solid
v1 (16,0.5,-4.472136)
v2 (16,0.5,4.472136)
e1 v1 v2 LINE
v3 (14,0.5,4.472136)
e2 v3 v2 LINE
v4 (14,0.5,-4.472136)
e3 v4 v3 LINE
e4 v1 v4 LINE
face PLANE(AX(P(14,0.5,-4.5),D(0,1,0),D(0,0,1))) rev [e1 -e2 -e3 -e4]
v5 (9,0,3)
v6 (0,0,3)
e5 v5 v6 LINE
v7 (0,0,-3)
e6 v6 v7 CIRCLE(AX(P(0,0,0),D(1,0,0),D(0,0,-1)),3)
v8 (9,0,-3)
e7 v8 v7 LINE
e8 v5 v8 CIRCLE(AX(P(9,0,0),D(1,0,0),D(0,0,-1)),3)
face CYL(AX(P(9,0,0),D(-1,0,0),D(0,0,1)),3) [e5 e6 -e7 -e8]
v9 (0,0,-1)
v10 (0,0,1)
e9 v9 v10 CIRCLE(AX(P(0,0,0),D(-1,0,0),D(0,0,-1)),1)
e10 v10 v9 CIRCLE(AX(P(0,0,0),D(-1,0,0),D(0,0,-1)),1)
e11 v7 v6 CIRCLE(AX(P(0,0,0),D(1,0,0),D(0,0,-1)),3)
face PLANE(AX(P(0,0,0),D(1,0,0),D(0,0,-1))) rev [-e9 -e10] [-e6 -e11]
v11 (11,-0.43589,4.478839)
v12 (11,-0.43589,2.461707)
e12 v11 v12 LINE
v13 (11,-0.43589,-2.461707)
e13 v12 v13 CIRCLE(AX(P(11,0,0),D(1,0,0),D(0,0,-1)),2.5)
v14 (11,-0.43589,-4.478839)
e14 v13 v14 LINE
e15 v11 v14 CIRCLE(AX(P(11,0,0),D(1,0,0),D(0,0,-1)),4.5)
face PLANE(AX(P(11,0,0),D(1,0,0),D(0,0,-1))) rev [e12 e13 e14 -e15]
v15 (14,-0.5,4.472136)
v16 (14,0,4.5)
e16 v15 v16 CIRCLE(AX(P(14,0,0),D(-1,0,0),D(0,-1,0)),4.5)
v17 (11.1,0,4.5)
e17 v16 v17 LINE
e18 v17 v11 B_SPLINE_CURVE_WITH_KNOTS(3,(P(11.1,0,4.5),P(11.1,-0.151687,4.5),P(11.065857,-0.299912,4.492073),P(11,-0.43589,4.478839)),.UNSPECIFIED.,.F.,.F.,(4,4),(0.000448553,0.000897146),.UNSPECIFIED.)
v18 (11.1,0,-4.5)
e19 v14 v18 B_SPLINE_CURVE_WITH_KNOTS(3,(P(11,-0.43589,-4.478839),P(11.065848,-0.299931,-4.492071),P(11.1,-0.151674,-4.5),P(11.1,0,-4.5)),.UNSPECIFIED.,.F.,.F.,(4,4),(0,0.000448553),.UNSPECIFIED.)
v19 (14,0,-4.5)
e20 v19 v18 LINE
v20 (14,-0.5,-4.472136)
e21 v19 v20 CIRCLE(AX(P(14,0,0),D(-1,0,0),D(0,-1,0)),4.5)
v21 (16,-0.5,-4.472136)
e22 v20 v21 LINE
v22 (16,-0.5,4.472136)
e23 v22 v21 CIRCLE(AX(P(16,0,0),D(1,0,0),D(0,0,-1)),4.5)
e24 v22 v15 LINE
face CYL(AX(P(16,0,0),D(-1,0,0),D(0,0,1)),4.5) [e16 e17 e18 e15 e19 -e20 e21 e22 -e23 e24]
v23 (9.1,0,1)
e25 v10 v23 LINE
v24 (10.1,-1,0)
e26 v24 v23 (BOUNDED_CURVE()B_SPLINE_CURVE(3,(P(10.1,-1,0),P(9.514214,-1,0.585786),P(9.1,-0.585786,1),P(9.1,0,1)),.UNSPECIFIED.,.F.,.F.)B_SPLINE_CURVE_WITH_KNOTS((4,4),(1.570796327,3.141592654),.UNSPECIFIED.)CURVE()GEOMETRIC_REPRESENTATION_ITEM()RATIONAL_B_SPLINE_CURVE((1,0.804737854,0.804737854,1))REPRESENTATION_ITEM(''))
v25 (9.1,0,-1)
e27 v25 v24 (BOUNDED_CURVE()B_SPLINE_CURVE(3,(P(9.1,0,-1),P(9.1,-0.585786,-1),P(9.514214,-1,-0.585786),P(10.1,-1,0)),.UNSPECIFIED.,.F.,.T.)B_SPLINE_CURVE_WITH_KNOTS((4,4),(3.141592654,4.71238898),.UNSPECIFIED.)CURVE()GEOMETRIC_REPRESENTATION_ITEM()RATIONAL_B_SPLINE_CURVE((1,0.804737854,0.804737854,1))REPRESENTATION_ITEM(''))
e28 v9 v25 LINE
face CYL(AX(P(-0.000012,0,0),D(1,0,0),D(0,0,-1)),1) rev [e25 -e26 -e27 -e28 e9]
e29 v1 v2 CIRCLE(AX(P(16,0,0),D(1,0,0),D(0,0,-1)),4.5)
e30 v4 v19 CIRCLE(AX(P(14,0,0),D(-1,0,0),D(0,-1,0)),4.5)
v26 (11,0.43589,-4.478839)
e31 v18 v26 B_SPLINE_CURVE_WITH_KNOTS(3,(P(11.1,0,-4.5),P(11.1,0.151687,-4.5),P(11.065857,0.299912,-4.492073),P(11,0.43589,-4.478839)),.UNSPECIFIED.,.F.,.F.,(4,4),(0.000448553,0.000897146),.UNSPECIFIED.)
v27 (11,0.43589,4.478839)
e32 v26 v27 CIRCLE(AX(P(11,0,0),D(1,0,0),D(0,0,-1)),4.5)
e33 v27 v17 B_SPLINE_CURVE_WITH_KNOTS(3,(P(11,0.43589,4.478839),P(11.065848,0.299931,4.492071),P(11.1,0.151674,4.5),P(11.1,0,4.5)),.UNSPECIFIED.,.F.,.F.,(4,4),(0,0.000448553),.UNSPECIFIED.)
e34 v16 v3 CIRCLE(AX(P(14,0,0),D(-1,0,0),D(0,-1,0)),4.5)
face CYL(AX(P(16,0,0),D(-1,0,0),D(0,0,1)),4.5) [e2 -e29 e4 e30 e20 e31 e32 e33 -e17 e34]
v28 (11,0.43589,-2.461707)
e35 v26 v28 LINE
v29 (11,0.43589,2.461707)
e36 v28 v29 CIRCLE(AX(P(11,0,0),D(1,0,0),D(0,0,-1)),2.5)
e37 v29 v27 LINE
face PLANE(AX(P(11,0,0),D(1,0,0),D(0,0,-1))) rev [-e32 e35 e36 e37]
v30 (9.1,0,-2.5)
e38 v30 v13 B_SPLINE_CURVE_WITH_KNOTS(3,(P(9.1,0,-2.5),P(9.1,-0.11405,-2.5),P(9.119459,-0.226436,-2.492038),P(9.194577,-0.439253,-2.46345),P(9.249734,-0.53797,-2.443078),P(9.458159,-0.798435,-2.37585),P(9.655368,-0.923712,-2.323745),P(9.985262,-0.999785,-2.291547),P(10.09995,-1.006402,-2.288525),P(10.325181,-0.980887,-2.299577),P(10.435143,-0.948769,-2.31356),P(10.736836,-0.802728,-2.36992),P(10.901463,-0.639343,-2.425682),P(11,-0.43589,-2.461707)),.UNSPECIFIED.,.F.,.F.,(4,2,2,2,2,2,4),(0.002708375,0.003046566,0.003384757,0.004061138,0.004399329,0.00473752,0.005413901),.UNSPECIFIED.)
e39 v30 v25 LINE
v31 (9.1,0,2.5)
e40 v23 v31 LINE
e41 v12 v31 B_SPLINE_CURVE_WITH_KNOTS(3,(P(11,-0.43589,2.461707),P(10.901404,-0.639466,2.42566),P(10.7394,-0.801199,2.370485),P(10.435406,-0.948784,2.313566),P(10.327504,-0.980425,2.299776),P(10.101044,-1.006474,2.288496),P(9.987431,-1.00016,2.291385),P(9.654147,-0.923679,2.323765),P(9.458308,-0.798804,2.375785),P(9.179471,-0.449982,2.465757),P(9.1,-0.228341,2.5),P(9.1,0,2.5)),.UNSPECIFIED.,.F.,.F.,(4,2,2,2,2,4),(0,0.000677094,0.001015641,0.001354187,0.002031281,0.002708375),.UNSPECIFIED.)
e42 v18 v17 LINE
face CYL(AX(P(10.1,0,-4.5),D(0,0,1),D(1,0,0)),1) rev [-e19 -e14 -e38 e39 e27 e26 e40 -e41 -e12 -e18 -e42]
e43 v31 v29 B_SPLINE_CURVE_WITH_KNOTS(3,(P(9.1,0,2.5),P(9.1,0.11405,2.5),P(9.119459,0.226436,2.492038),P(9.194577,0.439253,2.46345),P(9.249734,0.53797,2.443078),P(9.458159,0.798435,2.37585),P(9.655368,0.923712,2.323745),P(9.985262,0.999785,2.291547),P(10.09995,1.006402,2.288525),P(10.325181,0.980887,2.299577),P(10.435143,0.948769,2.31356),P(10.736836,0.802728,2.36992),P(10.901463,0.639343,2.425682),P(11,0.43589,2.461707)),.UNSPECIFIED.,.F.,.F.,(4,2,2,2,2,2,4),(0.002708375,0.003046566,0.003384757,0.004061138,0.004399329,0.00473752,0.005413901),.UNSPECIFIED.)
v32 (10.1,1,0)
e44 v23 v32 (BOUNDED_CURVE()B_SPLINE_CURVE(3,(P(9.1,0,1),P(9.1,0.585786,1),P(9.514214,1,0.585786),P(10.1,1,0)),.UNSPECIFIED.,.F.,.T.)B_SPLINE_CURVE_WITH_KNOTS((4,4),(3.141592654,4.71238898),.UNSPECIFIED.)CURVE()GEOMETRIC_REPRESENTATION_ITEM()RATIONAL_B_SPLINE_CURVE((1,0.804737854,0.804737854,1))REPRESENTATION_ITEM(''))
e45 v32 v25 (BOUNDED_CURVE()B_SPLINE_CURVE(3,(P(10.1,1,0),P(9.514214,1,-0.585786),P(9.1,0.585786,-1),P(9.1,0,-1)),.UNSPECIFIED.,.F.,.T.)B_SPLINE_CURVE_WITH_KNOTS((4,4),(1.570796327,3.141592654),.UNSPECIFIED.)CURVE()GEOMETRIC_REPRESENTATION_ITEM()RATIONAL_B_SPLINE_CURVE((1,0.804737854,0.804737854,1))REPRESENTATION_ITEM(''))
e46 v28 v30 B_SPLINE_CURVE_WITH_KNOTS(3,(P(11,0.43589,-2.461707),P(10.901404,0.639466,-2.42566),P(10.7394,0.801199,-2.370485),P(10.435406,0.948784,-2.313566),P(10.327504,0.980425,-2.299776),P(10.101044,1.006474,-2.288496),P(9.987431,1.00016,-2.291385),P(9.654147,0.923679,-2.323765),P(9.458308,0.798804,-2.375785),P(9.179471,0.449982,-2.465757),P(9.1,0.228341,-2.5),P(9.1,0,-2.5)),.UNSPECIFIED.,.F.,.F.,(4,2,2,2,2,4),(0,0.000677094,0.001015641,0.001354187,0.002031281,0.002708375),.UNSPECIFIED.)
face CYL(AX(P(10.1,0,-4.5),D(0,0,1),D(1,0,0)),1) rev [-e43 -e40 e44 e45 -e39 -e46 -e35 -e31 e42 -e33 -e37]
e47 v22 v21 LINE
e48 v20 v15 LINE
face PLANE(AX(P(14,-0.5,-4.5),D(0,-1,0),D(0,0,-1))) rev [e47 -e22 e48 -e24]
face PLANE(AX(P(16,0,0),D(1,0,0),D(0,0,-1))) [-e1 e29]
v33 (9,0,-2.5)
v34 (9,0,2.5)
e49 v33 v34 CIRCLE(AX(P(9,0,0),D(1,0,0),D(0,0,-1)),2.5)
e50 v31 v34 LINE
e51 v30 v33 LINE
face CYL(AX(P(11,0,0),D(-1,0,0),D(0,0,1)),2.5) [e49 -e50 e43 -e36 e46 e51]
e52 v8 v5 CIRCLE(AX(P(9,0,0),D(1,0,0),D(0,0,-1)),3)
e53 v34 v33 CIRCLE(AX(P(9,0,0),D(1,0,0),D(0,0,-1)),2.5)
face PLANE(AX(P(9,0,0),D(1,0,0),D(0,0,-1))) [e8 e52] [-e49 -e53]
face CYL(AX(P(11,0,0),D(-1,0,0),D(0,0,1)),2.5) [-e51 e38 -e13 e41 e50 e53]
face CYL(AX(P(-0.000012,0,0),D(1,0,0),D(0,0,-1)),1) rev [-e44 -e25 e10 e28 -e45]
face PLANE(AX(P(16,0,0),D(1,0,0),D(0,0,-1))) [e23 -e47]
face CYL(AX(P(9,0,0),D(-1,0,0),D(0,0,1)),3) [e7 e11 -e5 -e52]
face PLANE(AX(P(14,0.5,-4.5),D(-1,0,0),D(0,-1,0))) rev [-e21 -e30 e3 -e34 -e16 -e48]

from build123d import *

# Parameters (mm, degrees)
SKETCH1_R               = 3
BOSS_EXTRUDE1_DEPTH     = 9
SKETCH2_R               = 2.5
BOSS_EXTRUDE2_DEPTH     = 2
SKETCH3_R               = 4.5
BOSS_EXTRUDE3_DEPTH     = 5
CUT_EXTRUDE1_DEPTH      = 18.219175358
CUT_EXTRUDE1_DEPTH_BACK = 10.1
SKETCH4_R               = 1
CUT_EXTRUDE2_DEPTH      = 18.219175358
CUT_EXTRUDE2_DEPTH_BACK = 18.219175358
SKETCH6_R               = 1
CUT_EXTRUDE3_DEPTH      = 18.219175503
CUT_EXTRUDE3_DEPTH_BACK = 18.219175503
SKETCH7_W               = 4
SKETCH7_H               = 1


with BuildPart() as part:
    # Sketch1 → Boss-Extrude1 (new body)
    with BuildSketch(Plane(origin=(0, 0, 0), x_dir=(0, 0, -1), z_dir=(1, 0, 0))):
        Circle(SKETCH1_R)
    extrude(amount=BOSS_EXTRUDE1_DEPTH)

    # Sketch2 → Boss-Extrude2 (add)
    with BuildSketch(Plane(origin=(9, 0, 0), x_dir=(0, 0, -1), z_dir=(1, 0, 0))):
        Circle(SKETCH2_R)
    extrude(amount=BOSS_EXTRUDE2_DEPTH)

    # Sketch3 → Boss-Extrude3 (add)
    with BuildSketch(Plane(origin=(11, 0, 0), x_dir=(0, 0, -1), z_dir=(1, 0, 0))):
        Circle(SKETCH3_R)
    extrude(amount=BOSS_EXTRUDE3_DEPTH)

    # Sketch4 → Cut-Extrude1 (cut, two sides: drawn at the far end of the back side and taken through both)
    with BuildSketch(Plane.ZY.offset(-CUT_EXTRUDE1_DEPTH_BACK)):
        with Locations(Location((0, 0, 0), (0, 0, 180))):
            Circle(SKETCH4_R)
    extrude(amount=CUT_EXTRUDE1_DEPTH + CUT_EXTRUDE1_DEPTH_BACK, mode=Mode.SUBTRACT)

    # Sketch6 → Cut-Extrude2 (cut, two sides: drawn at the far end of the back side and taken through both)
    with BuildSketch(Plane.XY.offset(-CUT_EXTRUDE2_DEPTH_BACK)):
        with Locations(Location((10.1, 0, 0), (0, 0, 334.158067237))):
            Circle(SKETCH6_R)
    extrude(amount=CUT_EXTRUDE2_DEPTH + CUT_EXTRUDE2_DEPTH_BACK, mode=Mode.SUBTRACT)

    # Sketch7 → Cut-Extrude3 (cut, two sides: drawn at the far end of the back side and taken through both)
    with BuildSketch(Plane.XY.offset(-CUT_EXTRUDE3_DEPTH_BACK)):
        with Locations((16, 0)):
            Rectangle(SKETCH7_W, SKETCH7_H)
    extrude(amount=CUT_EXTRUDE3_DEPTH + CUT_EXTRUDE3_DEPTH_BACK, mode=Mode.SUBTRACT)


solid = part.part
